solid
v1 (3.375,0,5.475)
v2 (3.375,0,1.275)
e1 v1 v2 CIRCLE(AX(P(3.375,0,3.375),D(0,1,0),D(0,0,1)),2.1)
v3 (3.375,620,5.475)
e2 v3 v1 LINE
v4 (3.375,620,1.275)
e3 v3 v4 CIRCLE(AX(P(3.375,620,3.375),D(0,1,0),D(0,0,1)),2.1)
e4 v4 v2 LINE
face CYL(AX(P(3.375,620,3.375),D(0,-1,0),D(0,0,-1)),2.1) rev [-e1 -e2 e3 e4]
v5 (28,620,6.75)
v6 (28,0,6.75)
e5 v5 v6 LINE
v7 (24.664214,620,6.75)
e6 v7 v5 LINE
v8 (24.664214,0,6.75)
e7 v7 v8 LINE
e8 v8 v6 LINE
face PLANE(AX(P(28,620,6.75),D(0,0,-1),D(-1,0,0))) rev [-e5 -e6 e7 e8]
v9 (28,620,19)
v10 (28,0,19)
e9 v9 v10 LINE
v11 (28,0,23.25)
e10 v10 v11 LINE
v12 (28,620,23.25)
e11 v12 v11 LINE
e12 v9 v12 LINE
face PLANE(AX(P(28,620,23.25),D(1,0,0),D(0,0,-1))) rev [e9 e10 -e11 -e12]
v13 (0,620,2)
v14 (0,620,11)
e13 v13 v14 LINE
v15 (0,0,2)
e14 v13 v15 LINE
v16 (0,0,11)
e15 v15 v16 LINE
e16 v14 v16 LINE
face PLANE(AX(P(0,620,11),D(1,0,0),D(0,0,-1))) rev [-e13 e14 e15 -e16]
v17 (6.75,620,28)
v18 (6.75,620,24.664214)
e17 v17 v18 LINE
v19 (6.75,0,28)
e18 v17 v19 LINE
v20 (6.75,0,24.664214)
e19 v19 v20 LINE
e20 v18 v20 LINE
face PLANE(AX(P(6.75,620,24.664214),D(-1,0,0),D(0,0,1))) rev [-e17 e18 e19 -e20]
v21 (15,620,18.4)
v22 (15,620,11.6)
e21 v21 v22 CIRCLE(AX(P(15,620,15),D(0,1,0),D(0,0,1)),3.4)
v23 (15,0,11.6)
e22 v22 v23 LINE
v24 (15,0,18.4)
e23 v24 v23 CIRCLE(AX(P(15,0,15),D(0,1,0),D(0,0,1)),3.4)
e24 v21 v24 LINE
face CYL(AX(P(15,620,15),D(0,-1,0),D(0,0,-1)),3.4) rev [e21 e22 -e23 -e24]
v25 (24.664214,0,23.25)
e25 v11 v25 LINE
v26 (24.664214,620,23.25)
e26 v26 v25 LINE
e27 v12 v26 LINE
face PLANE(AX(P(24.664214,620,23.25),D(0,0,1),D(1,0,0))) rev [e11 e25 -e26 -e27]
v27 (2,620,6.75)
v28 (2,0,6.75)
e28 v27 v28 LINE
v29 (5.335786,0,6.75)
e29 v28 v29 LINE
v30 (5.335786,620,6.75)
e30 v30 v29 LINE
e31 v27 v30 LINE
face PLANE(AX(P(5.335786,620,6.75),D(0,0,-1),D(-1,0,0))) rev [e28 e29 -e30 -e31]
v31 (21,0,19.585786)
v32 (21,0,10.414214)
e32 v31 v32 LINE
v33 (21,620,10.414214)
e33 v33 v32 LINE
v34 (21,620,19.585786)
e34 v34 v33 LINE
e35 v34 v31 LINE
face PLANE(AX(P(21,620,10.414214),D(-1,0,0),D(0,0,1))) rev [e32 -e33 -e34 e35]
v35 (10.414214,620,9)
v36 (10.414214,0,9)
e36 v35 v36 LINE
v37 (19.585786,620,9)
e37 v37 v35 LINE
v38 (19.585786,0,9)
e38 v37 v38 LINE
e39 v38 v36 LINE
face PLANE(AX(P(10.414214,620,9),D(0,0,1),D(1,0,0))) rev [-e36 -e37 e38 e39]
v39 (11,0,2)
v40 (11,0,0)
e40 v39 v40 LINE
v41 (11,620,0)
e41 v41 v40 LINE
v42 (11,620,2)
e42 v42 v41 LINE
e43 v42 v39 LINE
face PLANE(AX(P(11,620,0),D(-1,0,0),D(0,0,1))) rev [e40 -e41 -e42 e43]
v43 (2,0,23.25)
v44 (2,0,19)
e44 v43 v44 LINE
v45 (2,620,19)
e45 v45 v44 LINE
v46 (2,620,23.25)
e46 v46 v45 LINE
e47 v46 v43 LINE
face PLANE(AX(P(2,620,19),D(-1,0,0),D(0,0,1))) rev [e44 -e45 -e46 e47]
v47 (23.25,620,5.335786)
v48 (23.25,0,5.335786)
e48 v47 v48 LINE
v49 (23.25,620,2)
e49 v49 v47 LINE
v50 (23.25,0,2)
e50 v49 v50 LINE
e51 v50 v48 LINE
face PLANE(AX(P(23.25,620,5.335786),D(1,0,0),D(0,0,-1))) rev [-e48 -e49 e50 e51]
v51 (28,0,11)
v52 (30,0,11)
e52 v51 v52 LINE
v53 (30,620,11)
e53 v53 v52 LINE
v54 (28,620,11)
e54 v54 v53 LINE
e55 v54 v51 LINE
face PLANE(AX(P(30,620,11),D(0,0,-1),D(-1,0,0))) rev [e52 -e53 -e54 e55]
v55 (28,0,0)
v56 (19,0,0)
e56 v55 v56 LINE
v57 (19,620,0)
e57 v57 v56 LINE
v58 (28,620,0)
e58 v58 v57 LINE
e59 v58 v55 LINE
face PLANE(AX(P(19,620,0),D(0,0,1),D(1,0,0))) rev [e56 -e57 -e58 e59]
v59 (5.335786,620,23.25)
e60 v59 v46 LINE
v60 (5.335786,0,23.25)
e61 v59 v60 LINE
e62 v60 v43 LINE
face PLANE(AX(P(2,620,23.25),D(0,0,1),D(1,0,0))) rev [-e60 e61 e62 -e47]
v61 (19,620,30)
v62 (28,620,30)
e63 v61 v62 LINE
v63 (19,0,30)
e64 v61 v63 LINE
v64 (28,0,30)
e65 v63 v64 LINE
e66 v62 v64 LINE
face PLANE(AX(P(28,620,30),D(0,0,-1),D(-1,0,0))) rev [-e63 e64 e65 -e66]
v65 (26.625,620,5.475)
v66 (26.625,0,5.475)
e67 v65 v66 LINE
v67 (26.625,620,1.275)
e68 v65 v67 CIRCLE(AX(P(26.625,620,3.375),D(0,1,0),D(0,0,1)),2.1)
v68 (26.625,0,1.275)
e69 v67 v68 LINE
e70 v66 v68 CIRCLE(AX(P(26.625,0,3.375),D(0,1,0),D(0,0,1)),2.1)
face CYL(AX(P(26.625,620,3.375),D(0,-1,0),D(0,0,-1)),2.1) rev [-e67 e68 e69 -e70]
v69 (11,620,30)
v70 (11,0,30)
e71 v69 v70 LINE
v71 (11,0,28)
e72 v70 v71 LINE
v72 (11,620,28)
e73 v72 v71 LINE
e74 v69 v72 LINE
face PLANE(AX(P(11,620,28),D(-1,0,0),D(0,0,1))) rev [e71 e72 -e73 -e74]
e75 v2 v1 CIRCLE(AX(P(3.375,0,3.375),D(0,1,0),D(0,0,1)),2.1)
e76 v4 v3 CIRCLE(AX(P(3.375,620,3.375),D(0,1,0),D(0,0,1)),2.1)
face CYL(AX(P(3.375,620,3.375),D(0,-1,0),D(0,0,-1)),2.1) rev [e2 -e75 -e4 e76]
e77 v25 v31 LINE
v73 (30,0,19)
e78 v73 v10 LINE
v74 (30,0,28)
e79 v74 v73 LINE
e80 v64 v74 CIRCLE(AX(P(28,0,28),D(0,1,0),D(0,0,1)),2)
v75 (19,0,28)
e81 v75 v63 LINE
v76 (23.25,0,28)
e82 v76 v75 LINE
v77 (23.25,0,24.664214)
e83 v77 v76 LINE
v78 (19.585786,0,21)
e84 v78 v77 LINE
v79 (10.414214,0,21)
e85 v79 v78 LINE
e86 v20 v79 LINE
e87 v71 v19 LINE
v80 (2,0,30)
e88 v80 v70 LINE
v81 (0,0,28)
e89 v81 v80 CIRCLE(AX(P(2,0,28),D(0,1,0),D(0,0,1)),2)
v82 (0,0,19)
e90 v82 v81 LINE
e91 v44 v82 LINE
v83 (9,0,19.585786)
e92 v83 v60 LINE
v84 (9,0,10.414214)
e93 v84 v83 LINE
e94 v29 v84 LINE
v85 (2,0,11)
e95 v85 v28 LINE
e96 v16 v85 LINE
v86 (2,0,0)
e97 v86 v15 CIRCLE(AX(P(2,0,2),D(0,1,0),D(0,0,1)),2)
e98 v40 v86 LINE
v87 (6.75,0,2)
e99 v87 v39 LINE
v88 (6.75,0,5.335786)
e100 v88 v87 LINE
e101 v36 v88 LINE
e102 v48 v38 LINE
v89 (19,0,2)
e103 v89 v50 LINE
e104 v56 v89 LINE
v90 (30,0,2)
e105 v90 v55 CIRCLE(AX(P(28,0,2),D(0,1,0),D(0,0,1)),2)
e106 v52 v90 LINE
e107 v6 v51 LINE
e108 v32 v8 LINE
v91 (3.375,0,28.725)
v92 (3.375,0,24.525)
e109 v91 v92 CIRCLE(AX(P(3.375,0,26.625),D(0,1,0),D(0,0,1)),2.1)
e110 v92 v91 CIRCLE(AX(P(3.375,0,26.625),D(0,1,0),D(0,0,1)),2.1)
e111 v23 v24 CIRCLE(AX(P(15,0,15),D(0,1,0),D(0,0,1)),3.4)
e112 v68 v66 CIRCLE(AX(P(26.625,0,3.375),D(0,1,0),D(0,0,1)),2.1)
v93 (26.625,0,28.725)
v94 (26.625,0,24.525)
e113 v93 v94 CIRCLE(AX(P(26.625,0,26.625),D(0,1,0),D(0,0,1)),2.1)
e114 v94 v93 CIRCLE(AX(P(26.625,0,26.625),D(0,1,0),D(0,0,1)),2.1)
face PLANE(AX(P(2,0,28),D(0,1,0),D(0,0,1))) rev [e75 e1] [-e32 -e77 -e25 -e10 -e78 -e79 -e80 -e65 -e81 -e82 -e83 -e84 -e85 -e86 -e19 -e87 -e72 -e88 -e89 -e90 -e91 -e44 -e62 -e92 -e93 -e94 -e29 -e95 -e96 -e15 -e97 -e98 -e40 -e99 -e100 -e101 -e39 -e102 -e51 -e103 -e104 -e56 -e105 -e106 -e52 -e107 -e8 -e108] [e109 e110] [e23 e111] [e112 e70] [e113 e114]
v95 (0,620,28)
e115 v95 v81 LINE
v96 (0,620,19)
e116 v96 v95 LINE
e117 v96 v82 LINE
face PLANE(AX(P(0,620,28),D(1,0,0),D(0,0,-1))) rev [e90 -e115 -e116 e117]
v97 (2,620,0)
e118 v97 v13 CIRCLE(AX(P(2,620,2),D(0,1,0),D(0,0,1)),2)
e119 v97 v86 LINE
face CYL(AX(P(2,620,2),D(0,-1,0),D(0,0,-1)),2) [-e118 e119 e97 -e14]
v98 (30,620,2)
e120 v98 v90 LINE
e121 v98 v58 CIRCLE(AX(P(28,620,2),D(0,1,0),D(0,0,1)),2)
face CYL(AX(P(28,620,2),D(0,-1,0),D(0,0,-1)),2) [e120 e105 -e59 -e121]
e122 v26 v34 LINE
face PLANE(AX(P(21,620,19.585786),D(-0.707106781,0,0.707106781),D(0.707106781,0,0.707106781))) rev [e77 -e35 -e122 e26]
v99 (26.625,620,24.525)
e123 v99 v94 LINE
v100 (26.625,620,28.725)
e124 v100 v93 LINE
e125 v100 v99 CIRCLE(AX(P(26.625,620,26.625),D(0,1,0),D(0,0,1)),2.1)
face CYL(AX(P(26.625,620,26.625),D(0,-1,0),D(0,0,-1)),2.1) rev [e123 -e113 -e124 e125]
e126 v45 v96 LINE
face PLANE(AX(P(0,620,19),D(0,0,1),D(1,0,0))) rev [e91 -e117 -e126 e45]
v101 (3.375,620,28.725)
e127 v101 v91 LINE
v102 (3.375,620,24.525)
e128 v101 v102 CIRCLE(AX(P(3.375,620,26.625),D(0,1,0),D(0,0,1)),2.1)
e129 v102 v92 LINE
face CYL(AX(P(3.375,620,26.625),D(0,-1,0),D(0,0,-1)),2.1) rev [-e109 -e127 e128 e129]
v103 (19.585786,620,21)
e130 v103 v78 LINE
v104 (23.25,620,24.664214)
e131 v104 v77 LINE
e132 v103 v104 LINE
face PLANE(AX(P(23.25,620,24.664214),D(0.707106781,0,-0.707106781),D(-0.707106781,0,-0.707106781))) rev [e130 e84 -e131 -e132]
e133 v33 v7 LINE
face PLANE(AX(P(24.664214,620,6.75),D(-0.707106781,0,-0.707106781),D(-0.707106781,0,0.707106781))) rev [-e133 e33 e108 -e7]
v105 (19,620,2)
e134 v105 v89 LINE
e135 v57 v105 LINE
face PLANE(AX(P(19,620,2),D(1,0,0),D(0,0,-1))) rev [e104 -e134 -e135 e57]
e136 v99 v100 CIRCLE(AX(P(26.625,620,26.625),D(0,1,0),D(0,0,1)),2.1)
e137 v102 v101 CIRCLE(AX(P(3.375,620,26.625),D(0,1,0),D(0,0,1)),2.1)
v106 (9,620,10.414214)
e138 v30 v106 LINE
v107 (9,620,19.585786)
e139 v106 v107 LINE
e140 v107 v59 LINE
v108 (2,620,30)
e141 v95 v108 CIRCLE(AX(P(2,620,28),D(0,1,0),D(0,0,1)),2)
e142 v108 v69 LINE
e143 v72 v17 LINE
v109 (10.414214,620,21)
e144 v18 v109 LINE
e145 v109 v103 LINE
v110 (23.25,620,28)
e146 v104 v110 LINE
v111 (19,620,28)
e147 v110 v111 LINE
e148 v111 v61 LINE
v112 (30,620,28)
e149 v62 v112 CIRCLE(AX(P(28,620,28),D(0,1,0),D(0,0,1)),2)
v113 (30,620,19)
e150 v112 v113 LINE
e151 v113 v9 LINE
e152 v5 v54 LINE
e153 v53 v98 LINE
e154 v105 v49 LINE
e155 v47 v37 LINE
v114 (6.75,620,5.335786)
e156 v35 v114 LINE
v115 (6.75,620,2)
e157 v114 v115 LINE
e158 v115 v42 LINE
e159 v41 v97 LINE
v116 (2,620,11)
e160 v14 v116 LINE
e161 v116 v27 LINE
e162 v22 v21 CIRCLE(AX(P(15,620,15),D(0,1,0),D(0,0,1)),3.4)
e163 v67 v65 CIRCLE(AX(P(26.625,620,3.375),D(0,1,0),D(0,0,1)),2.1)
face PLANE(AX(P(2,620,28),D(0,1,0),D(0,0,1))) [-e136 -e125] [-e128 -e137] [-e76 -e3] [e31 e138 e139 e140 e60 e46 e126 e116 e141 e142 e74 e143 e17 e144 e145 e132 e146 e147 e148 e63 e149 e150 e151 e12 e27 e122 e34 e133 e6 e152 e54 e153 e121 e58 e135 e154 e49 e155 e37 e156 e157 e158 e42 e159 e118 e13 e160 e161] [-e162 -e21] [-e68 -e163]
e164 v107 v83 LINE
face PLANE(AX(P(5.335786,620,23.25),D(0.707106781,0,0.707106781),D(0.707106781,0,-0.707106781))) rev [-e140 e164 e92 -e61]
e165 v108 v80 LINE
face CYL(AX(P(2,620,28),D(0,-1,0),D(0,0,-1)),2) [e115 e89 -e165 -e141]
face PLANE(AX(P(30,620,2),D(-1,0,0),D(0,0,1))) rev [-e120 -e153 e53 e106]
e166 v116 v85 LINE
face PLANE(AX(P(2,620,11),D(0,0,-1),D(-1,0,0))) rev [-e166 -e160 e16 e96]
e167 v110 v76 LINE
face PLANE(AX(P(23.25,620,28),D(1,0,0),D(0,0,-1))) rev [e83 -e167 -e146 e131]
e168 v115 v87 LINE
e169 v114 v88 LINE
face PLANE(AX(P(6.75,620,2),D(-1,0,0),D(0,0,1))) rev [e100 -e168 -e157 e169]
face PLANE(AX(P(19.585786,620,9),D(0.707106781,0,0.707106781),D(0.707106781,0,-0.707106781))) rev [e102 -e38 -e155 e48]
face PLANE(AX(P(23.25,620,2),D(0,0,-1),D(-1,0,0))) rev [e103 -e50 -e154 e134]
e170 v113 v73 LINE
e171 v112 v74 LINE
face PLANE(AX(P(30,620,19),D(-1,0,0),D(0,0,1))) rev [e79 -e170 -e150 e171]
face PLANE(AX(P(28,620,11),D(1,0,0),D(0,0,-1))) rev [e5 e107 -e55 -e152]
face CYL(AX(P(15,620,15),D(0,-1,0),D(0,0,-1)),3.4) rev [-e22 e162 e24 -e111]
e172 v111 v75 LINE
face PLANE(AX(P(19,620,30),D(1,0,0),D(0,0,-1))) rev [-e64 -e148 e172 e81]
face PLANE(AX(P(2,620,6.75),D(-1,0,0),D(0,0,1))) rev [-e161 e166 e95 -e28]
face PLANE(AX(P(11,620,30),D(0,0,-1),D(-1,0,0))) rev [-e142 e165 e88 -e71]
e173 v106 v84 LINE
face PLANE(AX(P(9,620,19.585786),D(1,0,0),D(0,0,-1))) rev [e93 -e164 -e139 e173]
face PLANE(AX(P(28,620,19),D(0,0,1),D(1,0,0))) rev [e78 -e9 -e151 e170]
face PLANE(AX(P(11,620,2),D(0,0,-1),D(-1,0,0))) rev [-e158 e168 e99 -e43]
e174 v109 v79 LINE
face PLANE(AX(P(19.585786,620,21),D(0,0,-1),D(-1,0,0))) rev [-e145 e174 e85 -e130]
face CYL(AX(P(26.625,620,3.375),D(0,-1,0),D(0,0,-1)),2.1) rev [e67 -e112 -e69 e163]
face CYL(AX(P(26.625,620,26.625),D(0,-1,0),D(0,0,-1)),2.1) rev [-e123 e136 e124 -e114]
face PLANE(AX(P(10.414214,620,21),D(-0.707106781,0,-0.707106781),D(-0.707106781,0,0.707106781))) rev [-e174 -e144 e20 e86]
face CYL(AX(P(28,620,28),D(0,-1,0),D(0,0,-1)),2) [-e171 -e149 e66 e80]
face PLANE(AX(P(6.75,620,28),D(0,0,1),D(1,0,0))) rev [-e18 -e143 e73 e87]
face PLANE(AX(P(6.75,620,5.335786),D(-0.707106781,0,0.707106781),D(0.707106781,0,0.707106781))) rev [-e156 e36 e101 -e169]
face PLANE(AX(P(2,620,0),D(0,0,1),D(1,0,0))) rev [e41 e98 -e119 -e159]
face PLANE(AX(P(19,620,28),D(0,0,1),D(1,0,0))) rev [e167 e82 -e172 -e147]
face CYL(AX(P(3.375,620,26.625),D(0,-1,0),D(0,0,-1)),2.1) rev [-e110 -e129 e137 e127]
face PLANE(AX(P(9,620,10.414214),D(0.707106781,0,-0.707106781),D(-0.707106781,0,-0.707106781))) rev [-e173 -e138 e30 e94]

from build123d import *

# Parameters (mm, degrees)
SKETCH_1_R      = 2.1
SKETCH_1_R_2    = 3.4
EXTRUDE_1_DEPTH = 620


with BuildPart() as part:
    # 草图1 → 拉伸1 (new body)
    with BuildSketch(Plane(origin=(0, 0, 0), x_dir=(1, 0, 0), z_dir=(0, 1, 0))):
        with BuildLine():
            Line((6.75, -28), (11, -28))
            Line((11, -28), (11, -30))
            Line((11, -30), (2, -30))
            ThreePointArc((2, -30), (0.585786438, -29.414213562), (0, -28))
            Line((0, -28), (0, -19))
            Line((0, -19), (2, -19))
            Line((2, -19), (2, -23.25))
            Line((2, -23.25), (5.335785999, -23.25))
            Line((5.335785999, -23.25), (9, -19.585785999))
            Line((9, -19.585785999), (9, -10.414214001))
            Line((9, -10.414214001), (5.335785999, -6.75))
            Line((5.335785999, -6.75), (2, -6.75))
            Line((2, -6.75), (2, -11))
            Line((2, -11), (0, -11))
            Line((0, -11), (0, -2))
            ThreePointArc((0, -2), (0.585786438, -0.585786438), (2, 0))
            Line((2, 0), (11, 0))
            Line((11, 0), (11, -2))
            Line((11, -2), (6.75, -2))
            Line((6.75, -2), (6.75, -5.335785999))
            Line((6.75, -5.335785999), (10.414214001, -9))
            Line((10.414214001, -9), (19.585785999, -9))
            Line((19.585785999, -9), (23.25, -5.335785999))
            Line((23.25, -5.335785999), (23.25, -2))
            Line((23.25, -2), (19, -2))
            Line((19, -2), (19, 0))
            Line((19, 0), (28, 0))
            ThreePointArc((28, 0), (29.414213562, -0.585786438), (30, -2))
            Line((30, -2), (30, -11))
            Line((30, -11), (28, -11))
            Line((28, -11), (28, -6.75))
            Line((28, -6.75), (24.664214001, -6.75))
            Line((24.664214001, -6.75), (21, -10.414214001))
            Line((21, -10.414214001), (21, -19.585785999))
            Line((21, -19.585785999), (24.664214001, -23.25))
            Line((24.664214001, -23.25), (28, -23.25))
            Line((28, -23.25), (28, -19))
            Line((28, -19), (30, -19))
            Line((30, -19), (30, -28))
            ThreePointArc((30, -28), (29.414213562, -29.414213562), (28, -30))
            Line((28, -30), (19, -30))
            Line((19, -30), (19, -28))
            Line((19, -28), (23.25, -28))
            Line((23.25, -28), (23.25, -24.664214001))
            Line((23.25, -24.664214001), (19.585785999, -21))
            Line((19.585785999, -21), (10.414214001, -21))
            Line((10.414214001, -21), (6.75, -24.664214001))
            Line((6.75, -24.664214001), (6.75, -28))
        make_face()
        with Locations(Location((3.375, -26.625, 0), (0, 0, 270))):
            Circle(SKETCH_1_R, mode=Mode.SUBTRACT)
        with Locations(Location((26.625, -26.625, 0), (0, 0, 270))):
            Circle(SKETCH_1_R, mode=Mode.SUBTRACT)
        with Locations(Location((15, -15, 0), (0, 0, 270))):
            Circle(SKETCH_1_R_2, mode=Mode.SUBTRACT)
        with Locations(Location((3.375, -3.375, 0), (0, 0, 270))):
            Circle(SKETCH_1_R, mode=Mode.SUBTRACT)
        with Locations(Location((26.625, -3.375, 0), (0, 0, 270))):
            Circle(SKETCH_1_R, mode=Mode.SUBTRACT)
    extrude(amount=EXTRUDE_1_DEPTH)


solid = part.part
